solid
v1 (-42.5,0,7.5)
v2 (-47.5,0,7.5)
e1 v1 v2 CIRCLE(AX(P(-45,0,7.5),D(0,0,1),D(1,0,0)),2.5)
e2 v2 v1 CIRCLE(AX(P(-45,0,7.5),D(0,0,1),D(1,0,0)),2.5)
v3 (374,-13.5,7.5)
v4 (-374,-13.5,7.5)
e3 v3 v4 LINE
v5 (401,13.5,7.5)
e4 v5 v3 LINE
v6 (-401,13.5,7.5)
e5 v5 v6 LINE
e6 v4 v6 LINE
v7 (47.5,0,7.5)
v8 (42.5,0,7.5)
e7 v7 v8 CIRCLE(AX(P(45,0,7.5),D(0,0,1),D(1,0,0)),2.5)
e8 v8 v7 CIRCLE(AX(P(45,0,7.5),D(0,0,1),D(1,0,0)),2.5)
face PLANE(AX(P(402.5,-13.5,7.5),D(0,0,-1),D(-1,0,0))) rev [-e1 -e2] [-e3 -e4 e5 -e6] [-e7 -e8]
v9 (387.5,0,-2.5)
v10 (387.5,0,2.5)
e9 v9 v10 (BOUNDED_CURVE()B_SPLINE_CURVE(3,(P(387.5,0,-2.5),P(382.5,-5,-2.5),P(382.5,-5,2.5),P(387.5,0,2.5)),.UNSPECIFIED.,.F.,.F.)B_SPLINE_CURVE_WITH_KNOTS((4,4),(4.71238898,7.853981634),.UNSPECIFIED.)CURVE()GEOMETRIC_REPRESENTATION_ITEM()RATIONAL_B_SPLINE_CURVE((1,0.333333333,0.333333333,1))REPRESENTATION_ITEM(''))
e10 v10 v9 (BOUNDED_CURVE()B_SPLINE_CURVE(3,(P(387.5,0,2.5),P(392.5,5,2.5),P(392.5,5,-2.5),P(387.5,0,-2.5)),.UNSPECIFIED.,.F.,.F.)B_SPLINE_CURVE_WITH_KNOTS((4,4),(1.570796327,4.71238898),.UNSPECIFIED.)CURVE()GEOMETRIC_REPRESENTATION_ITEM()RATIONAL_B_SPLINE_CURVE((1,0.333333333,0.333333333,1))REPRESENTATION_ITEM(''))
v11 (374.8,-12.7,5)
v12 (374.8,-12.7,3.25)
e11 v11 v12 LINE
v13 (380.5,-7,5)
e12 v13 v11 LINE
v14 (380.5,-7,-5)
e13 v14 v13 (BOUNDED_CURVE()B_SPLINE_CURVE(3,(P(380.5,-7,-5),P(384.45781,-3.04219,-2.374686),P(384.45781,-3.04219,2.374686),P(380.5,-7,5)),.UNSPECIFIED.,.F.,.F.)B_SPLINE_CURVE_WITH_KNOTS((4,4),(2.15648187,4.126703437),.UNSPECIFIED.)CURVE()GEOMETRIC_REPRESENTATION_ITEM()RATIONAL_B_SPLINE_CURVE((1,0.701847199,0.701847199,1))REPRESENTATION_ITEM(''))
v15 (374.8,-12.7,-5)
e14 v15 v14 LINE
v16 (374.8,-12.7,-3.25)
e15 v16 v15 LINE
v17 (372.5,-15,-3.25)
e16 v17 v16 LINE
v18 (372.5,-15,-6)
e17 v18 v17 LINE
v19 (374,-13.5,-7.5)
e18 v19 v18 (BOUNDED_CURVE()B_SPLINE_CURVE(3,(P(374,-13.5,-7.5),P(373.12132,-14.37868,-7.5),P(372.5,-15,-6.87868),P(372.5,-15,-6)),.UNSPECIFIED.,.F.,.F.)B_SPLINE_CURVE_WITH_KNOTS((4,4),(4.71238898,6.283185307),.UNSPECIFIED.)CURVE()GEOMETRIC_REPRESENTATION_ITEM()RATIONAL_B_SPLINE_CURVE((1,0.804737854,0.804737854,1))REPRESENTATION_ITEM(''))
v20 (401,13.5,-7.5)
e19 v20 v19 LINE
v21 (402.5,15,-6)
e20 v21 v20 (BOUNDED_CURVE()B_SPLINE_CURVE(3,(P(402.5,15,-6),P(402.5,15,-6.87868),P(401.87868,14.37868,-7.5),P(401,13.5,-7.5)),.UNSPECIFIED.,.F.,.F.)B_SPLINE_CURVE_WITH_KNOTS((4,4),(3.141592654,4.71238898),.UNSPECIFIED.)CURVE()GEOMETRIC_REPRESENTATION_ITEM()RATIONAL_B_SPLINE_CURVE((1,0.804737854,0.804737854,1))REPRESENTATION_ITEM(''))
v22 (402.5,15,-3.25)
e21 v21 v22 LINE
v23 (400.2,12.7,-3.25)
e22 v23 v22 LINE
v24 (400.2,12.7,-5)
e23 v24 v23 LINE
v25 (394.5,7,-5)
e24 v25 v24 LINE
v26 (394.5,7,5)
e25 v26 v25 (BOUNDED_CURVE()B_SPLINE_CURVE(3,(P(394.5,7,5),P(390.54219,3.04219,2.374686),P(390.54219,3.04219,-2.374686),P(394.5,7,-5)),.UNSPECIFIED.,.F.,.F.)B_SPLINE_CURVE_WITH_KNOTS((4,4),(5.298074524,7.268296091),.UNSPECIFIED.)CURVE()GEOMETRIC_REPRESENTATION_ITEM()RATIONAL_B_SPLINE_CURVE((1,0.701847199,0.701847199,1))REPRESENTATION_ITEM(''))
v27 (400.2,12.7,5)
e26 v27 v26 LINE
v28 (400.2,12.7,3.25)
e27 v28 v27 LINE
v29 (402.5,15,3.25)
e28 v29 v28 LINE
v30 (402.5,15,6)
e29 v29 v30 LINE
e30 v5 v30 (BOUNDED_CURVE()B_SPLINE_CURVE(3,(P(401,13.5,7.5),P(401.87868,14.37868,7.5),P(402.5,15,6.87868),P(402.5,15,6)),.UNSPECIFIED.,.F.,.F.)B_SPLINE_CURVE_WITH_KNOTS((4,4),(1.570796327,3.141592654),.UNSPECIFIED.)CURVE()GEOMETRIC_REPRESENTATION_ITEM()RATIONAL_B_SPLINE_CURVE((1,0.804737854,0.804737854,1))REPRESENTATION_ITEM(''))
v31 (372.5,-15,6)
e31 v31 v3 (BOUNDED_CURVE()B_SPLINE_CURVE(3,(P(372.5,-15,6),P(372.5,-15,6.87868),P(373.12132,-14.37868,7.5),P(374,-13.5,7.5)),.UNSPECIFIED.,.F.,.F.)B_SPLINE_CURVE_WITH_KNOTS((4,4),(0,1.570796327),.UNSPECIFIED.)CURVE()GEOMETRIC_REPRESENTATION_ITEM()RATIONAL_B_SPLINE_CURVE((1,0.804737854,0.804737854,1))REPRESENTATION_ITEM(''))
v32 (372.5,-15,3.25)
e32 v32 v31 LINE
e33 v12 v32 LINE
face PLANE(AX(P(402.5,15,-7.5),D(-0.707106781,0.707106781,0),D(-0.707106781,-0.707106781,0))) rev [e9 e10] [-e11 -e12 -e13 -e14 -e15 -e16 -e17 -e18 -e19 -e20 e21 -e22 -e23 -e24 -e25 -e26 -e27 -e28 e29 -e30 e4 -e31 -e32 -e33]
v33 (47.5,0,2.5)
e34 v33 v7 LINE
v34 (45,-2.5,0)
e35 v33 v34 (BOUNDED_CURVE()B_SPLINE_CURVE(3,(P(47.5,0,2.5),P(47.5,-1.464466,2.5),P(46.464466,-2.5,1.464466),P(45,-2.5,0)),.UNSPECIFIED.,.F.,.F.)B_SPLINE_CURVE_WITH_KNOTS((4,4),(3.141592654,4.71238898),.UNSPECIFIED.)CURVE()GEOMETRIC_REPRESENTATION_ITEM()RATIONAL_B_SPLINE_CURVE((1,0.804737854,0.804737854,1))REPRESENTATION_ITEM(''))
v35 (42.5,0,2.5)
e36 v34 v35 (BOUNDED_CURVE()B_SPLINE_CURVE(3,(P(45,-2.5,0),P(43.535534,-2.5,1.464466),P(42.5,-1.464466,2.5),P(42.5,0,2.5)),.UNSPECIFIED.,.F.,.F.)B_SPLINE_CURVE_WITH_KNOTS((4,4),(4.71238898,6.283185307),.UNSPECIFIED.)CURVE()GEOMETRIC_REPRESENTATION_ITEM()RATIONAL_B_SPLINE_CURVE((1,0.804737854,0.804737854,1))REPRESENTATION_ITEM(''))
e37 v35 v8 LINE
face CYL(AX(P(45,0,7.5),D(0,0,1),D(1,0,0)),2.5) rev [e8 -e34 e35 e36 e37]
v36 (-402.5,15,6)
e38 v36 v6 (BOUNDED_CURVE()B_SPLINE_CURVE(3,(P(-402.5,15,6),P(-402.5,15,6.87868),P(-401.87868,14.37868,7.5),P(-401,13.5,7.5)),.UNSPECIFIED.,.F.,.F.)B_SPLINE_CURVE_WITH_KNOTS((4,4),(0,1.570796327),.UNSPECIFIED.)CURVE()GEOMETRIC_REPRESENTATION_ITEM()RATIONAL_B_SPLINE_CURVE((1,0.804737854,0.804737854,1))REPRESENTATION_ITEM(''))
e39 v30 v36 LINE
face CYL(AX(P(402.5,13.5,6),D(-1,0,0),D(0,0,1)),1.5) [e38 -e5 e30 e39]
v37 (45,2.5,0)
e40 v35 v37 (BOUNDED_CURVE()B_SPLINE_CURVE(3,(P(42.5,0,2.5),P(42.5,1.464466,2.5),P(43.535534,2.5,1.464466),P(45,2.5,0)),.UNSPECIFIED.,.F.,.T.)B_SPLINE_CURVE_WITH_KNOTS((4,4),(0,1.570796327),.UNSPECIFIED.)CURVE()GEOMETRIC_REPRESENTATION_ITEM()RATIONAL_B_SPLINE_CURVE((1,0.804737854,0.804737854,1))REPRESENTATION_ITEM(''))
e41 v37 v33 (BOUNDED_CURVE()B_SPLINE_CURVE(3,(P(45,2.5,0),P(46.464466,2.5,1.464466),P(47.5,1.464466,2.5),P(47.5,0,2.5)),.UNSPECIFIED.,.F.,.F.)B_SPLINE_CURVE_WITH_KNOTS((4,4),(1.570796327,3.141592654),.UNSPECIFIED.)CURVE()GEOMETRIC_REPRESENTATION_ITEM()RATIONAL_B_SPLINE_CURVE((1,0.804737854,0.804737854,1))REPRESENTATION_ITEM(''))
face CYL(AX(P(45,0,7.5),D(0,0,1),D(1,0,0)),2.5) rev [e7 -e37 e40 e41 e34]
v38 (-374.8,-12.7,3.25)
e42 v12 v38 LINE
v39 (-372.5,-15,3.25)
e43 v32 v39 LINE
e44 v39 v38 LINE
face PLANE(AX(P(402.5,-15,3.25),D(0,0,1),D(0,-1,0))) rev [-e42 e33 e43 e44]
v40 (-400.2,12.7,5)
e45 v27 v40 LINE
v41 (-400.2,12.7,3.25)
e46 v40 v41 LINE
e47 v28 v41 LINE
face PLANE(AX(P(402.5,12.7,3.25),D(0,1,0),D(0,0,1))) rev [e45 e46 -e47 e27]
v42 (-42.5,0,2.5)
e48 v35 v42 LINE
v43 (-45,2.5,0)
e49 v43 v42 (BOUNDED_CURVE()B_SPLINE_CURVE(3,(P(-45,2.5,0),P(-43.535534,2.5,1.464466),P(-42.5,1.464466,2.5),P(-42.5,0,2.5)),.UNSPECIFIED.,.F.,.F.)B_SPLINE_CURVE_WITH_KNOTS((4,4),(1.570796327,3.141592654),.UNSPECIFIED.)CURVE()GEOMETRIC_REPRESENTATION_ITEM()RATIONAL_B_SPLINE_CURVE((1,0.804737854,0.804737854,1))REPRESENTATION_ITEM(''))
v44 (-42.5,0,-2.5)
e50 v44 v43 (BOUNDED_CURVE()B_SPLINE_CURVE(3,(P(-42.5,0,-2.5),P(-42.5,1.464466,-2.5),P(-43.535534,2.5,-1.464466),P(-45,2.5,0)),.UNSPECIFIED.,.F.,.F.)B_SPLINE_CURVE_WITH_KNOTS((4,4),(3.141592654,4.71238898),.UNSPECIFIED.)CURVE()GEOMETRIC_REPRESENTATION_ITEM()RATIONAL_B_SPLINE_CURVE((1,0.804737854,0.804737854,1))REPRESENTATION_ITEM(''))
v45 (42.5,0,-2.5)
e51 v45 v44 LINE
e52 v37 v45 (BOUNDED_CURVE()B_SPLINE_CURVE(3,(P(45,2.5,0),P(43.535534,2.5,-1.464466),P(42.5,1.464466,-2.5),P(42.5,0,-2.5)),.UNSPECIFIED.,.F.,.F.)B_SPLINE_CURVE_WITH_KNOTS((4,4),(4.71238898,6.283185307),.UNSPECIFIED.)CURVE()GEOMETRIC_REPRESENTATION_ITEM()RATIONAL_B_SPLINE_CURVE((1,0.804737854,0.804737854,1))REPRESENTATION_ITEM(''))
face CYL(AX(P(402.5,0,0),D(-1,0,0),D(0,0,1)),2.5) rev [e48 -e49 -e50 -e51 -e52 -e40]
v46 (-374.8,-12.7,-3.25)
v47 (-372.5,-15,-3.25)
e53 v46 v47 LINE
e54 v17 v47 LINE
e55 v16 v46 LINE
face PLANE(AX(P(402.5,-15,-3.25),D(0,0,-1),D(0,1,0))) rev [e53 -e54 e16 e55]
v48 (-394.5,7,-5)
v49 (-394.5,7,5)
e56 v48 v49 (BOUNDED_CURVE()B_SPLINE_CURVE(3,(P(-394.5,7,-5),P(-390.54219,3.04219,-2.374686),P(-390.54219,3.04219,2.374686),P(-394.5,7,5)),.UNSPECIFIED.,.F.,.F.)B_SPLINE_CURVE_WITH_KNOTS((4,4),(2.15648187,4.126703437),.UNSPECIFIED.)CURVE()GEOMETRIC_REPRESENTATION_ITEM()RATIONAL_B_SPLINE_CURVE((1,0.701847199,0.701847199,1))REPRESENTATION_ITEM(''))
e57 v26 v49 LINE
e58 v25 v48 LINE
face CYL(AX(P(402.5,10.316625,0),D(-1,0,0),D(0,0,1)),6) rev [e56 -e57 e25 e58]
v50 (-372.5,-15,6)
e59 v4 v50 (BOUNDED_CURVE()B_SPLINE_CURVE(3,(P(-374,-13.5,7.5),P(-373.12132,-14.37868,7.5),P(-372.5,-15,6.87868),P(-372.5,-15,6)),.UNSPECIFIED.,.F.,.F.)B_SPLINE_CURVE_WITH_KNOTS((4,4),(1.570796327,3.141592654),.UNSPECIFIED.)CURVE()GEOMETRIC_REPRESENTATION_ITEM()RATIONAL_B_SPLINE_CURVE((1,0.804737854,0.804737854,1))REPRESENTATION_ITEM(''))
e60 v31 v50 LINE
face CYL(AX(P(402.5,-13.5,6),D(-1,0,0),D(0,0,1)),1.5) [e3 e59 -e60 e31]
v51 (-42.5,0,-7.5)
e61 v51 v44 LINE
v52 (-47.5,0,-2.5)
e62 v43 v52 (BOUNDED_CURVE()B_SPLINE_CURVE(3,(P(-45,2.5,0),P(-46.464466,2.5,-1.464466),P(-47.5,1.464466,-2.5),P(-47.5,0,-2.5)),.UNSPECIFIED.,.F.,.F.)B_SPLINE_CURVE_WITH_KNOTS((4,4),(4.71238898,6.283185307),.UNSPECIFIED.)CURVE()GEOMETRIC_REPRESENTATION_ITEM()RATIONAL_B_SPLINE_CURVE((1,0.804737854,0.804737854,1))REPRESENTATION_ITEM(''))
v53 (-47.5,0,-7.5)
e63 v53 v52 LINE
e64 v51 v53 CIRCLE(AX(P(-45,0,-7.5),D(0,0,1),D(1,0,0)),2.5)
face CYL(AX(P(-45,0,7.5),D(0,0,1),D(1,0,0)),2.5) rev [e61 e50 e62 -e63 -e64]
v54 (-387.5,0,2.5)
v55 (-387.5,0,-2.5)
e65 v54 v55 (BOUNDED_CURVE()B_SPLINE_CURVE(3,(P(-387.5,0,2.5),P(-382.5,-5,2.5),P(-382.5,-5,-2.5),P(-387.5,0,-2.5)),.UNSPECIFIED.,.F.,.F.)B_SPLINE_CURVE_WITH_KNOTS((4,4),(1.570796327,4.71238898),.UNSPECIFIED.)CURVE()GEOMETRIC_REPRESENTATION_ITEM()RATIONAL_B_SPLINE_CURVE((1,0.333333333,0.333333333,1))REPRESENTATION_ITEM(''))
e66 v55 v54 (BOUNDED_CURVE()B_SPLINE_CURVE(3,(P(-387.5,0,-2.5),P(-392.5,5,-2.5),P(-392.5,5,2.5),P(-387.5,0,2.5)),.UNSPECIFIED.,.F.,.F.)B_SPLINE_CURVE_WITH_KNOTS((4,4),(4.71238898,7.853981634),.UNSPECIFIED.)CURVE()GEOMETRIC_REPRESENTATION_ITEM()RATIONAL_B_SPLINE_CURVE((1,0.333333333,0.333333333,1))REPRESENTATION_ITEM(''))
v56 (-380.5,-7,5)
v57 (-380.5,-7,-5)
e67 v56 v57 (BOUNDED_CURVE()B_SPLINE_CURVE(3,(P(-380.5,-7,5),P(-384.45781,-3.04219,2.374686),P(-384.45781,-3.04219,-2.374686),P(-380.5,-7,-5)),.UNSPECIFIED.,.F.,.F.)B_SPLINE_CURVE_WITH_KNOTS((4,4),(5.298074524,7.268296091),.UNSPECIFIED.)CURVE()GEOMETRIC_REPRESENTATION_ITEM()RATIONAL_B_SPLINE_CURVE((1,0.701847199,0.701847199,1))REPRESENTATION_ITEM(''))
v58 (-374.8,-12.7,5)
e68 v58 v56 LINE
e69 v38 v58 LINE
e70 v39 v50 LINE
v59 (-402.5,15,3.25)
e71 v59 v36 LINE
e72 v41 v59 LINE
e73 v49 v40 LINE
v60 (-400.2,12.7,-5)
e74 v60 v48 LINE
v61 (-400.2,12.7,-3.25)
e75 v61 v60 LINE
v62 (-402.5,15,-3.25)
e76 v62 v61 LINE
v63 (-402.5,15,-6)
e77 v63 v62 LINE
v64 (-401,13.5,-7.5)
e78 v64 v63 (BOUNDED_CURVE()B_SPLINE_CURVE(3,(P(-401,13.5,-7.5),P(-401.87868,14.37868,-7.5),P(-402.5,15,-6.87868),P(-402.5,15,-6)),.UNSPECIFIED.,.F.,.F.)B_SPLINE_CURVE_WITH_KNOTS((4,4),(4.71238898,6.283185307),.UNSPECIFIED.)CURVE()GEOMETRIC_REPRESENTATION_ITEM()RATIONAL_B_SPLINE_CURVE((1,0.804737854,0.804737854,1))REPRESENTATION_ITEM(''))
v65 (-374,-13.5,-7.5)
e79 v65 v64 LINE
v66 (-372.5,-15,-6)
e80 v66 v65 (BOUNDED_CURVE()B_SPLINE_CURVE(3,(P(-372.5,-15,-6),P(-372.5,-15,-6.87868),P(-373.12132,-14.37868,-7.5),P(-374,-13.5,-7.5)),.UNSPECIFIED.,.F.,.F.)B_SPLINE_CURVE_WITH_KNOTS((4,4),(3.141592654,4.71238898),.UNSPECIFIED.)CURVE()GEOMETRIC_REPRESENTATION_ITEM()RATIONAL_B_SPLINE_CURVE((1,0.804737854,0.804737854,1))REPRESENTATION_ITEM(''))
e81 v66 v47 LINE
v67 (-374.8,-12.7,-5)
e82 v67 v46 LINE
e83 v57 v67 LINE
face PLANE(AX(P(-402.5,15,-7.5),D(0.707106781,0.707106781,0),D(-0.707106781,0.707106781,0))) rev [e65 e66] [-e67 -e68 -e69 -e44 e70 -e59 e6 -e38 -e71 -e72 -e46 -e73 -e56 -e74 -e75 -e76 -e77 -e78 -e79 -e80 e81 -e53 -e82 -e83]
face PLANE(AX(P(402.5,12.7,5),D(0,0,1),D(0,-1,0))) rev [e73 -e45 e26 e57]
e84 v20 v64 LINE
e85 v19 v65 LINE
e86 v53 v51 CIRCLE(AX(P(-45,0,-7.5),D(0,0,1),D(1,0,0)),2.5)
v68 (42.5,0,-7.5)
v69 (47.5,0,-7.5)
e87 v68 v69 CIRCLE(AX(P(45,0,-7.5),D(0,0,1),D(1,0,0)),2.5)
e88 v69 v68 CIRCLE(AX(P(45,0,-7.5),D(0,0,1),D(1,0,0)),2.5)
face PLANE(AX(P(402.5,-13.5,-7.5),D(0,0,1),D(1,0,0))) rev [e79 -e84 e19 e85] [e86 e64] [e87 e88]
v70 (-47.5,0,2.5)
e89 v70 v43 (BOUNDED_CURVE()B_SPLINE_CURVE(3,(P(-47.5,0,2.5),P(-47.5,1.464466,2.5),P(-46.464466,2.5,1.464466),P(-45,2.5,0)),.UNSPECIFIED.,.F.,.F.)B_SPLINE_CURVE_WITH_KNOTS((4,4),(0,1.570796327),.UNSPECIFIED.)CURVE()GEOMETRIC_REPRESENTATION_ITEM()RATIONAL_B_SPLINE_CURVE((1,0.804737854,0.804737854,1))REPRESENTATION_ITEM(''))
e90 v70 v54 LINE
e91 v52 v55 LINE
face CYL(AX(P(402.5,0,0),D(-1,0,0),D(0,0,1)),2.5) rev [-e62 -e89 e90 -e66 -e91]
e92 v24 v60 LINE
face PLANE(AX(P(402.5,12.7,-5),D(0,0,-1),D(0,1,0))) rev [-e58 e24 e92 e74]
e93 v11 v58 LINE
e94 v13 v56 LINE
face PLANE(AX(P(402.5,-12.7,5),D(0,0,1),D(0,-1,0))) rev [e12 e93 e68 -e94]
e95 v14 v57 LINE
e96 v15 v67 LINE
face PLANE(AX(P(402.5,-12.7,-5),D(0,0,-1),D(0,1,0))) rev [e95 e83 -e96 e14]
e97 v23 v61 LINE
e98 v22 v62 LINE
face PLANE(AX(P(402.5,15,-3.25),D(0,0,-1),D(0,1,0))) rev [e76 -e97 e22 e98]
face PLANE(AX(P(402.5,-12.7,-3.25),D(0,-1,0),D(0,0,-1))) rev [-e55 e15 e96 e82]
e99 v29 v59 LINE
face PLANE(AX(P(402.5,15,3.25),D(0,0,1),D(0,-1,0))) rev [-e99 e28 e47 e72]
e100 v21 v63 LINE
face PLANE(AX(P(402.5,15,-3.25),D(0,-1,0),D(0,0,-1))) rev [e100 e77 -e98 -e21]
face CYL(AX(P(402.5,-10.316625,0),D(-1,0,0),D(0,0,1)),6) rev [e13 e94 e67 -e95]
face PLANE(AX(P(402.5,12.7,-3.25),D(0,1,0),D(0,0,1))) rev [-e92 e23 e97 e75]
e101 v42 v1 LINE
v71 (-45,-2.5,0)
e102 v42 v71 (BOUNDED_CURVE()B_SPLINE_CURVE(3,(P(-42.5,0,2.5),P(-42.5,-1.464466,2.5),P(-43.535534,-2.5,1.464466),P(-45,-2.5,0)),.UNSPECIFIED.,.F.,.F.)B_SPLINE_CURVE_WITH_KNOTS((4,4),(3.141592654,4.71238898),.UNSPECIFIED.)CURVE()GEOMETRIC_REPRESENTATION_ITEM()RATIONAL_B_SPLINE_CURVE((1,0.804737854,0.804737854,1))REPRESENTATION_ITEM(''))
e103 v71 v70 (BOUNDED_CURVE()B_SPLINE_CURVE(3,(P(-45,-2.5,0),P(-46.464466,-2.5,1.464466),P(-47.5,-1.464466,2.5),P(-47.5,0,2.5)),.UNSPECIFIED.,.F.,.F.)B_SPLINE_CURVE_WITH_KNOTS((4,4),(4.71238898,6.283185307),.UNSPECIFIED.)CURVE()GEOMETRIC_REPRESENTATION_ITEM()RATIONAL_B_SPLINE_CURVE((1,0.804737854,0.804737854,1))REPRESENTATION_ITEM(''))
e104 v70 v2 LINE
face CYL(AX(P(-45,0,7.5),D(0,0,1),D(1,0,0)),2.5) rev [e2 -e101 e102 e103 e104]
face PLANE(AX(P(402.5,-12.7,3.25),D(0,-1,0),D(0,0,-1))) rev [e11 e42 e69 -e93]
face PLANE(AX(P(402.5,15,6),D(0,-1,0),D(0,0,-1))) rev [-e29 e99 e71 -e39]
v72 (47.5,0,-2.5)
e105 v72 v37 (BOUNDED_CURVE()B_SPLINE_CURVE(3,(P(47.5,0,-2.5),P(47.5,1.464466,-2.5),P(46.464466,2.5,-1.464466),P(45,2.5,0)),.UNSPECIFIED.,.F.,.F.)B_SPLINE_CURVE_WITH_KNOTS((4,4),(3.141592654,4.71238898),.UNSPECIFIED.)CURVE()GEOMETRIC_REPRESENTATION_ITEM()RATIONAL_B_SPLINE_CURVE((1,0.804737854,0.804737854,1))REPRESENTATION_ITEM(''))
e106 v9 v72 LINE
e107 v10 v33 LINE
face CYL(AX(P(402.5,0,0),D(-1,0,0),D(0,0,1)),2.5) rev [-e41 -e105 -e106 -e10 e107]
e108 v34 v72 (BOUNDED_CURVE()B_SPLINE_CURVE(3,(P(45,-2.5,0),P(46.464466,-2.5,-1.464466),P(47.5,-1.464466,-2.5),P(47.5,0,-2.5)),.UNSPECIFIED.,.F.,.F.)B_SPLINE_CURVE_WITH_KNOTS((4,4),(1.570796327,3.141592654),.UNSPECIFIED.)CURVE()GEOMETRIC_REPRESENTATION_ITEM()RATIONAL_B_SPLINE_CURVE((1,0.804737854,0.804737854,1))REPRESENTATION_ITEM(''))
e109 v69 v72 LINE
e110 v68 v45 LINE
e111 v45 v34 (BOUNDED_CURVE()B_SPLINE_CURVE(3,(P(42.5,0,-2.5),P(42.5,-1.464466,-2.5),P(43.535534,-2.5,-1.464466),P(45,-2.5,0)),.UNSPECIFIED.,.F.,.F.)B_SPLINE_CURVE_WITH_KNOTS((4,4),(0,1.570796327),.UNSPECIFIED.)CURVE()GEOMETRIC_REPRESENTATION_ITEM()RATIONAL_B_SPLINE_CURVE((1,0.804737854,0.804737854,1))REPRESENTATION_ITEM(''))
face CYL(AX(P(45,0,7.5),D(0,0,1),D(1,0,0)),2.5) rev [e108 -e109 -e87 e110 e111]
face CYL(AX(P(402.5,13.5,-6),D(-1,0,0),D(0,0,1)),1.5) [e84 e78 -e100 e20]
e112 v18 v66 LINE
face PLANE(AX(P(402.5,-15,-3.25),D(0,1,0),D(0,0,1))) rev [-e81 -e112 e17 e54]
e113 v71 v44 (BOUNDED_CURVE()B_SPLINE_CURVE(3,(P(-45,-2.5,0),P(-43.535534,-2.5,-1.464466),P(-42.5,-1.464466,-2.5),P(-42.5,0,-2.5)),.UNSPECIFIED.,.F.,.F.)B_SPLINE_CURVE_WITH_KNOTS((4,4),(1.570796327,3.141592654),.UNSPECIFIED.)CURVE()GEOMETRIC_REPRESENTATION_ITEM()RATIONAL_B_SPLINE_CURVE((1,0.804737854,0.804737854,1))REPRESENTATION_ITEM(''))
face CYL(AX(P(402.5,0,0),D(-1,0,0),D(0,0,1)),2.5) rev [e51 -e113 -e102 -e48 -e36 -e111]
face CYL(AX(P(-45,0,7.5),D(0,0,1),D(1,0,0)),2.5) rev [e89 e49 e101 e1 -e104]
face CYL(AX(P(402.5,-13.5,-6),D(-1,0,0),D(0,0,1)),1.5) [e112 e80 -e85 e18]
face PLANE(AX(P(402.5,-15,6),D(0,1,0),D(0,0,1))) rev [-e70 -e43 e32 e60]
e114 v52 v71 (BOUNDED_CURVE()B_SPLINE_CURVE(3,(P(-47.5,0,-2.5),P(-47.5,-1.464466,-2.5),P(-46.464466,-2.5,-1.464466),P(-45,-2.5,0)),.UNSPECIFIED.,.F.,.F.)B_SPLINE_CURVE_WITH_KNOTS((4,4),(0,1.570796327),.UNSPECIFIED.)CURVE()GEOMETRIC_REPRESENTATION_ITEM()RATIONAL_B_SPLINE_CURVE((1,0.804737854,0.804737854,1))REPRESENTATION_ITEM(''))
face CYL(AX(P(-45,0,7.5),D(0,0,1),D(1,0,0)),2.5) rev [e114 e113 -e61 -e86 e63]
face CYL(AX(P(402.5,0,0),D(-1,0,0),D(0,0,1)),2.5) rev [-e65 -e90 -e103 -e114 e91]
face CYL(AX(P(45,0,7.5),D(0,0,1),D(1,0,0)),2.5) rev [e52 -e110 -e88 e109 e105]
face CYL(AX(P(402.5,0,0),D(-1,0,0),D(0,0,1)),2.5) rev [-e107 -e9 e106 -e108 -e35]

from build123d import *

# Parameters (mm, degrees)
SKETCH11_R          = 2.5
MEMBER_1_DEPTH      = 805
CUT_EXTRUDE_1_DEPTH = 404.058618566
HOLE_WIZARD_M6_1_D  = 5


with BuildPart() as part:
    # Sketch11 → Member 1 (new body)
    with BuildSketch(Plane(origin=(-402.5, 0, 0), x_dir=(0, 0, -1), z_dir=(1, 0, 0))):
        with BuildLine():
            Line((-6, -15), (-3.25, -15))
            Line((-3.25, -15), (-3.25, -12.7))
            Line((-3.25, -12.7), (-5, -12.7))
            Line((-5, -12.7), (-5, -7))
            ThreePointArc((-5, -7), (0, -4.31662479), (5, -7))
            Line((5, -7), (5, -12.7))
            Line((5, -12.7), (3.25, -12.7))
            Line((3.25, -12.7), (3.25, -15))
            Line((3.25, -15), (6, -15))
            ThreePointArc((6, -15), (7.060660172, -14.560660172), (7.5, -13.5))
            Line((7.5, -13.5), (7.5, 13.5))
            ThreePointArc((7.5, 13.5), (7.060660172, 14.560660172), (6, 15))
            Line((6, 15), (3.25, 15))
            Line((3.25, 15), (3.25, 12.7))
            Line((3.25, 12.7), (5, 12.7))
            Line((5, 12.7), (5, 7))
            ThreePointArc((5, 7), (0, 4.31662479), (-5, 7))
            Line((-5, 7), (-5, 12.7))
            Line((-5, 12.7), (-3.25, 12.7))
            Line((-3.25, 12.7), (-3.25, 15))
            Line((-3.25, 15), (-6, 15))
            ThreePointArc((-6, 15), (-7.060660172, 14.560660172), (-7.5, 13.5))
            Line((-7.5, 13.5), (-7.5, -13.5))
            ThreePointArc((-7.5, -13.5), (-7.060660172, -14.560660172), (-6, -15))
        make_face()
        Circle(SKETCH11_R, mode=Mode.SUBTRACT)
    extrude(amount=MEMBER_1_DEPTH)

    # 草图4 → 切除-拉伸1 (cut, through all)
    with BuildSketch(Plane.XY.offset(7.5)):
        Polygon((-402.5, 15), (-372.5, -15), (-402.5, -15), align=None)
        Polygon((402.5, -15), (402.5, 15), (372.5, -15), align=None)
    extrude(amount=-CUT_EXTRUDE_1_DEPTH, mode=Mode.SUBTRACT)

    # M6 螺纹孔1 (through all)
    with Locations(Plane.XY.offset(7.5)):
        with Locations((-45, 0), (45, 0)):
            Hole(HOLE_WIZARD_M6_1_D / 2)


solid = part.part
